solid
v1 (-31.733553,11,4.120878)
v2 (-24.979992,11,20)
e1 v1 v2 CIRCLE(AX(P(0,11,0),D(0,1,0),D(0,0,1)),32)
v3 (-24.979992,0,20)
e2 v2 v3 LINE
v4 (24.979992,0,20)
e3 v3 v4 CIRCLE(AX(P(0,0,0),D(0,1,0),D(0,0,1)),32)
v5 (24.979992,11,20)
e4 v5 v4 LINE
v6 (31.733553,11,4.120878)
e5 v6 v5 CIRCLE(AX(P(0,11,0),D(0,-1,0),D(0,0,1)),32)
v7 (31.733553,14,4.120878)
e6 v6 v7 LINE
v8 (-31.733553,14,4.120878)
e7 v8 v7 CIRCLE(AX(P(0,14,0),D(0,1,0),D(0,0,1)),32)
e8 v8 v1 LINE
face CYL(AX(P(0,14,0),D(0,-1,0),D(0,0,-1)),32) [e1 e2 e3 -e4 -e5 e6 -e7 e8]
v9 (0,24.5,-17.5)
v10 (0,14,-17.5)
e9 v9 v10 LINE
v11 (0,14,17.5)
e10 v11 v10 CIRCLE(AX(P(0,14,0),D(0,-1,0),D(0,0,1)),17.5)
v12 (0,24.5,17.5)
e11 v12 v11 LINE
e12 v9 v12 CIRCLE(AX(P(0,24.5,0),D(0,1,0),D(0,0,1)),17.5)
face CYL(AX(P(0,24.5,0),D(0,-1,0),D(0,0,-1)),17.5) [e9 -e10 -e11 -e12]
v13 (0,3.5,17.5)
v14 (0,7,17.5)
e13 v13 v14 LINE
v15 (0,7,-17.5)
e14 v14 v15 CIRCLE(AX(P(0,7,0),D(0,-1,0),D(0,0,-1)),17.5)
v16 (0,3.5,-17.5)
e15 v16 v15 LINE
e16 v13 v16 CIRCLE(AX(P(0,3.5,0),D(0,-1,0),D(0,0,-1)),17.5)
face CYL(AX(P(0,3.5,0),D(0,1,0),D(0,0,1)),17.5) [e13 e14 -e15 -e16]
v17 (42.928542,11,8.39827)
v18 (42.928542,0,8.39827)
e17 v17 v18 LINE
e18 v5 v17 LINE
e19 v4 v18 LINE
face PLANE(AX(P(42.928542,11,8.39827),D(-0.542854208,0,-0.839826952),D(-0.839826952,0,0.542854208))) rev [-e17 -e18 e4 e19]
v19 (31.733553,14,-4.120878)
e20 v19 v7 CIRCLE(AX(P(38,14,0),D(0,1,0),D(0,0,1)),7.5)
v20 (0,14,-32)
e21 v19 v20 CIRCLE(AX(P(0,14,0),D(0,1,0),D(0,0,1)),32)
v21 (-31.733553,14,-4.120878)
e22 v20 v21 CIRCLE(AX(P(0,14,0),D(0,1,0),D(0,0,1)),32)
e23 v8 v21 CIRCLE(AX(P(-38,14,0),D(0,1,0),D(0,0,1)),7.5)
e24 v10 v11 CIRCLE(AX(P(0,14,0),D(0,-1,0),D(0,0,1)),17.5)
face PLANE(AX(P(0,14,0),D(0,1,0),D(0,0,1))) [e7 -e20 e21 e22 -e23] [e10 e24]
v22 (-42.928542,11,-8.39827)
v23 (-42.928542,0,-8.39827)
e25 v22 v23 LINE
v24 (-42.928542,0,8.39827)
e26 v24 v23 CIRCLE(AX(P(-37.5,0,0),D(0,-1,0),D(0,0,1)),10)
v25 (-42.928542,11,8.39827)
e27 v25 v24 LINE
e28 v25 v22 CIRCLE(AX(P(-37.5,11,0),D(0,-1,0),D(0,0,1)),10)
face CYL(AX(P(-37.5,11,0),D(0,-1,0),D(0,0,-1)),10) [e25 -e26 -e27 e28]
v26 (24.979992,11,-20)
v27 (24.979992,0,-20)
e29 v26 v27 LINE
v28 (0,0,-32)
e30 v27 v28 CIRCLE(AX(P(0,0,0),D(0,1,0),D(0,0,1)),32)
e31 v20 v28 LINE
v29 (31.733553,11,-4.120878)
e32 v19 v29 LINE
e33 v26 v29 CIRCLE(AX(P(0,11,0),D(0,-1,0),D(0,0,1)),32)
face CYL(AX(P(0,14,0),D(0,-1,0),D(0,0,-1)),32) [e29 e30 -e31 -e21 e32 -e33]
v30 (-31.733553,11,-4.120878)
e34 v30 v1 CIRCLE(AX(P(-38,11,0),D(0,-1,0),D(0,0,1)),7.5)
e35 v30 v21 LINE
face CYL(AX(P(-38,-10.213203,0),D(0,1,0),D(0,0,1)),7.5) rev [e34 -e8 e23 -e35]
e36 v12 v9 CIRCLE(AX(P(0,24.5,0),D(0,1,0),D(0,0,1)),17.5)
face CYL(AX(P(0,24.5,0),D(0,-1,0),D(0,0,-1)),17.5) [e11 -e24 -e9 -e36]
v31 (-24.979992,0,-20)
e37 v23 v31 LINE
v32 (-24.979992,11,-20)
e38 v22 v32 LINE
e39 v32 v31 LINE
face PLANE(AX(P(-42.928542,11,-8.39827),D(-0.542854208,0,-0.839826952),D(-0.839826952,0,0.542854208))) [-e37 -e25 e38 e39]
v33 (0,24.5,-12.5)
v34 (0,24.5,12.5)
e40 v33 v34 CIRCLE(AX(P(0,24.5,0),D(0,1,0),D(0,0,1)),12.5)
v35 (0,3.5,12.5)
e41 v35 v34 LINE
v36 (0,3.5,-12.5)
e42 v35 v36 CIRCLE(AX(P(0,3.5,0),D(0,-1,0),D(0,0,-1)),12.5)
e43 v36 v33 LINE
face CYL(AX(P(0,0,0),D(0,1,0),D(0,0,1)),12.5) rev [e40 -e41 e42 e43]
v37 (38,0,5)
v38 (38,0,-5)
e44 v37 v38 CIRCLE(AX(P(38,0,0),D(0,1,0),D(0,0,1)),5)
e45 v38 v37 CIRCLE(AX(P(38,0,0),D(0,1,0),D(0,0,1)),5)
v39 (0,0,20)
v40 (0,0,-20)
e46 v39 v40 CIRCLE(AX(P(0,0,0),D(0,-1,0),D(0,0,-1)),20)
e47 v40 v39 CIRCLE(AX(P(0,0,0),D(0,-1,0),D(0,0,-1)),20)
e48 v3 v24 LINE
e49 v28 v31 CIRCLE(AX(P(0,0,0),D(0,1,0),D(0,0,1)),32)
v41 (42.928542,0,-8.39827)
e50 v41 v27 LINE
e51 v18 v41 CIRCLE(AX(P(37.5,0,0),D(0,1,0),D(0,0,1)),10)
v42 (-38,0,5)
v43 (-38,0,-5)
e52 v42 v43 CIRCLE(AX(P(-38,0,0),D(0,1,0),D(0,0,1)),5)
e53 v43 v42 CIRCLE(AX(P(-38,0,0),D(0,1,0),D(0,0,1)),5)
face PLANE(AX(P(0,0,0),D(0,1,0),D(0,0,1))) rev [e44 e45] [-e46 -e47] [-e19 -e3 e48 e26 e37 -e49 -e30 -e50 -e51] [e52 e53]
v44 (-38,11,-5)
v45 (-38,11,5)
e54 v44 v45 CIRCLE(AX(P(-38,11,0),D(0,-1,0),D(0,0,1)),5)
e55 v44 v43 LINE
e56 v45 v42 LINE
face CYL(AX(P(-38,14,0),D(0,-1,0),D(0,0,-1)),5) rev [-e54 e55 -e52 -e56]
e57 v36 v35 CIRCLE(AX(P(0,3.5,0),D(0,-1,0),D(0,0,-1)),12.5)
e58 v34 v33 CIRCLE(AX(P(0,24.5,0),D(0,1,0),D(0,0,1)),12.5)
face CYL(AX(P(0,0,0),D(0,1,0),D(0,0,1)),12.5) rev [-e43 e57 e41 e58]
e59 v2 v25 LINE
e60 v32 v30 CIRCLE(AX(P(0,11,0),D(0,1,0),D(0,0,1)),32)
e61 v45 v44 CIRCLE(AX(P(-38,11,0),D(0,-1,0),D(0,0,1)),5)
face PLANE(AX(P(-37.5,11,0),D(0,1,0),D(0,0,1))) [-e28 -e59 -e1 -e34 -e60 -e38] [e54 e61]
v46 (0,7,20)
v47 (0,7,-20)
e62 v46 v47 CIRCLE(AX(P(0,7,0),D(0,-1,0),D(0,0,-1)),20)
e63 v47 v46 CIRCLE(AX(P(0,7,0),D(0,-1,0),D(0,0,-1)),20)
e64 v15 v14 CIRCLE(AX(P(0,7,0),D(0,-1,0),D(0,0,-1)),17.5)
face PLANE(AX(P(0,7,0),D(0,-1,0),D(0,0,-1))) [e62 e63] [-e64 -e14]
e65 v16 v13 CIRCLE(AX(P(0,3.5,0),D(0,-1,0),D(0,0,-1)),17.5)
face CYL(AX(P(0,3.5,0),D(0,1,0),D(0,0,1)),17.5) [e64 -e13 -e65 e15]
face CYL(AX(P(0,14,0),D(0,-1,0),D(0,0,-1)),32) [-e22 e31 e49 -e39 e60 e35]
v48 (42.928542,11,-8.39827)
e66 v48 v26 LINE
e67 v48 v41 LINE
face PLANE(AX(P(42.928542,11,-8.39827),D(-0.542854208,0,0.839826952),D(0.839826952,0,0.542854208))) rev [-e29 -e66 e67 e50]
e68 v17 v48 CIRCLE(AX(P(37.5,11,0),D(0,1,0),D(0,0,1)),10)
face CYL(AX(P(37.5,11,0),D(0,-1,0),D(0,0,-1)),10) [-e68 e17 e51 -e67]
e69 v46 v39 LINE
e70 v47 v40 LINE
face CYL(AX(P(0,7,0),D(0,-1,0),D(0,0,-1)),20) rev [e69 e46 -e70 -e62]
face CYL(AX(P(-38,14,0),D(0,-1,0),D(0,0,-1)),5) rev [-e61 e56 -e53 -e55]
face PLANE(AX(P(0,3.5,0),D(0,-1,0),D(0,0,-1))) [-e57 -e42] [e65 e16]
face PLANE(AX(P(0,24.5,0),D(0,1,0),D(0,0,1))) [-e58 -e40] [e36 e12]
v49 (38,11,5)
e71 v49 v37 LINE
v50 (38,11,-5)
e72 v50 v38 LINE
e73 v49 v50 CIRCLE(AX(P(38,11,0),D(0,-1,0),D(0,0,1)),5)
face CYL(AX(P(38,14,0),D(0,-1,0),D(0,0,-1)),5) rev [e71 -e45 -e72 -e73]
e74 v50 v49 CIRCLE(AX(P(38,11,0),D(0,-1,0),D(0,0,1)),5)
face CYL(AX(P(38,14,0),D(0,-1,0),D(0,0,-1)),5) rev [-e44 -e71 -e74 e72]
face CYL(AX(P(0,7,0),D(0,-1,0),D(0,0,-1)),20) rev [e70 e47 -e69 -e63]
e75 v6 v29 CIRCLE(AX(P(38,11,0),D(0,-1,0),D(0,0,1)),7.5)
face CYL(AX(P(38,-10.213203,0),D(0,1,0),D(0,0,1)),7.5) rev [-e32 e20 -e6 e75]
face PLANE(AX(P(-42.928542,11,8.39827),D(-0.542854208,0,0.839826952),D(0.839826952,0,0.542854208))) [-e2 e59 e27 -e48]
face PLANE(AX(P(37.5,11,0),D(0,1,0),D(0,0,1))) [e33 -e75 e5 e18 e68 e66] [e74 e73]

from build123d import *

# Parameters (mm, degrees)
SKETCH_1_R          = 32
EXTRUDE_1_DEPTH     = 14
EXTRUDE_2_DEPTH     = 11
SKETCH_3_R          = 5
CUT_EXTRUDE_1_DEPTH = 59.959732021
SKETCH_4_R          = 7.5
CUT_EXTRUDE_2_DEPTH = 3
SKETCH_5_R          = 17.5
EXTRUDE_3_DEPTH     = 24.5
SKETCH_6_R          = 20
CUT_EXTRUDE_3_DEPTH = 7
EXTRUDE_START       = 3.5
SKETCH_7_R          = 17.5
EXTRUDE_4_DEPTH     = 3.5
SKETCH_8_R          = 12.5
CUT_EXTRUDE_4_DEPTH = 63.293659388


with BuildPart() as part:
    # 草图1 → 凸台-拉伸1 (new body)
    with BuildSketch(Plane(origin=(0, 0, 0), x_dir=(1, 0, 0), z_dir=(0, 1, 0))):
        with Locations(Location((0, 0, 0), (0, 0, 270))):
            Circle(SKETCH_1_R)
    extrude(amount=EXTRUDE_1_DEPTH)

    # 草图2 → 凸台-拉伸2 (add)
    with BuildSketch(Plane(origin=(0, 0, 0), x_dir=(1, 0, 0), z_dir=(0, 1, 0))):
        with BuildLine():
            Line((42.928542082, 8.398269516), (24.979991994, 20))
            ThreePointArc((24.979991994, 20), (32, 0), (24.979991994, -20))
            Line((24.979991994, -20), (42.928542082, -8.398269516))
            ThreePointArc((42.928542082, -8.398269516), (47.5, 0), (42.928542082, 8.398269516))
        make_face()
    extrude_2 = extrude(amount=EXTRUDE_2_DEPTH)

    # 镜向1: 凸台-拉伸2 across plane
    add(extrude_2.mirror(Plane(origin=(0, 0, 0), x_dir=(0, 0, 1), z_dir=(1, 0, 0))))

    # 草图3 → 切除-拉伸1 (cut, through all)
    with BuildSketch(Plane(origin=(0, 0, 0), x_dir=(1, 0, 0), z_dir=(0, 1, 0))):
        with Locations(Location((-38, 0, 0), (0, 0, 270))):
            Circle(SKETCH_3_R)
        with Locations(Location((38, 0, 0), (0, 0, 270))):
            Circle(SKETCH_3_R)
    extrude(amount=CUT_EXTRUDE_1_DEPTH, mode=Mode.SUBTRACT)

    # 草图4 → 切除-拉伸2 (cut)
    with BuildSketch(Plane(origin=(0, 14, 0), x_dir=(1, 0, 0), z_dir=(0, 1, 0))):
        with Locations((-38, 0)):
            Circle(SKETCH_4_R)
        with Locations((38, 0)):
            Circle(SKETCH_4_R)
    extrude(amount=-CUT_EXTRUDE_2_DEPTH, mode=Mode.SUBTRACT)

    # 草图5 → 凸台-拉伸3 (add)
    with BuildSketch(Plane(origin=(0, 0, 0), x_dir=(1, 0, 0), z_dir=(0, 1, 0))):
        with Locations(Location((0, 0, 0), (0, 0, 270))):
            Circle(SKETCH_5_R)
    extrude(amount=EXTRUDE_3_DEPTH)

    # 草图6 → 切除-拉伸3 (cut)
    with BuildSketch(Plane.XZ):
        with Locations(Location((0, 0, 0), (0, 0, 270))):
            Circle(SKETCH_6_R)
    extrude(amount=-CUT_EXTRUDE_3_DEPTH, mode=Mode.SUBTRACT)

    # 草图7 → 凸台-拉伸4 (add)
    with BuildSketch(Plane.XZ.offset(-7).offset(EXTRUDE_START)):
        with Locations(Location((0, 0, 0), (0, 0, 90))):
            Circle(SKETCH_7_R)
    extrude(amount=-EXTRUDE_4_DEPTH)

    # 草图8 → 切除-拉伸4 (cut, through all)
    with BuildSketch(Plane(origin=(0, 24.5, 0), x_dir=(1, 0, 0), z_dir=(0, 1, 0))):
        with Locations(Location((0, 0, 0), (0, 0, 270))):
            Circle(SKETCH_8_R)
    extrude(amount=-CUT_EXTRUDE_4_DEPTH, mode=Mode.SUBTRACT)


solid = part.part
